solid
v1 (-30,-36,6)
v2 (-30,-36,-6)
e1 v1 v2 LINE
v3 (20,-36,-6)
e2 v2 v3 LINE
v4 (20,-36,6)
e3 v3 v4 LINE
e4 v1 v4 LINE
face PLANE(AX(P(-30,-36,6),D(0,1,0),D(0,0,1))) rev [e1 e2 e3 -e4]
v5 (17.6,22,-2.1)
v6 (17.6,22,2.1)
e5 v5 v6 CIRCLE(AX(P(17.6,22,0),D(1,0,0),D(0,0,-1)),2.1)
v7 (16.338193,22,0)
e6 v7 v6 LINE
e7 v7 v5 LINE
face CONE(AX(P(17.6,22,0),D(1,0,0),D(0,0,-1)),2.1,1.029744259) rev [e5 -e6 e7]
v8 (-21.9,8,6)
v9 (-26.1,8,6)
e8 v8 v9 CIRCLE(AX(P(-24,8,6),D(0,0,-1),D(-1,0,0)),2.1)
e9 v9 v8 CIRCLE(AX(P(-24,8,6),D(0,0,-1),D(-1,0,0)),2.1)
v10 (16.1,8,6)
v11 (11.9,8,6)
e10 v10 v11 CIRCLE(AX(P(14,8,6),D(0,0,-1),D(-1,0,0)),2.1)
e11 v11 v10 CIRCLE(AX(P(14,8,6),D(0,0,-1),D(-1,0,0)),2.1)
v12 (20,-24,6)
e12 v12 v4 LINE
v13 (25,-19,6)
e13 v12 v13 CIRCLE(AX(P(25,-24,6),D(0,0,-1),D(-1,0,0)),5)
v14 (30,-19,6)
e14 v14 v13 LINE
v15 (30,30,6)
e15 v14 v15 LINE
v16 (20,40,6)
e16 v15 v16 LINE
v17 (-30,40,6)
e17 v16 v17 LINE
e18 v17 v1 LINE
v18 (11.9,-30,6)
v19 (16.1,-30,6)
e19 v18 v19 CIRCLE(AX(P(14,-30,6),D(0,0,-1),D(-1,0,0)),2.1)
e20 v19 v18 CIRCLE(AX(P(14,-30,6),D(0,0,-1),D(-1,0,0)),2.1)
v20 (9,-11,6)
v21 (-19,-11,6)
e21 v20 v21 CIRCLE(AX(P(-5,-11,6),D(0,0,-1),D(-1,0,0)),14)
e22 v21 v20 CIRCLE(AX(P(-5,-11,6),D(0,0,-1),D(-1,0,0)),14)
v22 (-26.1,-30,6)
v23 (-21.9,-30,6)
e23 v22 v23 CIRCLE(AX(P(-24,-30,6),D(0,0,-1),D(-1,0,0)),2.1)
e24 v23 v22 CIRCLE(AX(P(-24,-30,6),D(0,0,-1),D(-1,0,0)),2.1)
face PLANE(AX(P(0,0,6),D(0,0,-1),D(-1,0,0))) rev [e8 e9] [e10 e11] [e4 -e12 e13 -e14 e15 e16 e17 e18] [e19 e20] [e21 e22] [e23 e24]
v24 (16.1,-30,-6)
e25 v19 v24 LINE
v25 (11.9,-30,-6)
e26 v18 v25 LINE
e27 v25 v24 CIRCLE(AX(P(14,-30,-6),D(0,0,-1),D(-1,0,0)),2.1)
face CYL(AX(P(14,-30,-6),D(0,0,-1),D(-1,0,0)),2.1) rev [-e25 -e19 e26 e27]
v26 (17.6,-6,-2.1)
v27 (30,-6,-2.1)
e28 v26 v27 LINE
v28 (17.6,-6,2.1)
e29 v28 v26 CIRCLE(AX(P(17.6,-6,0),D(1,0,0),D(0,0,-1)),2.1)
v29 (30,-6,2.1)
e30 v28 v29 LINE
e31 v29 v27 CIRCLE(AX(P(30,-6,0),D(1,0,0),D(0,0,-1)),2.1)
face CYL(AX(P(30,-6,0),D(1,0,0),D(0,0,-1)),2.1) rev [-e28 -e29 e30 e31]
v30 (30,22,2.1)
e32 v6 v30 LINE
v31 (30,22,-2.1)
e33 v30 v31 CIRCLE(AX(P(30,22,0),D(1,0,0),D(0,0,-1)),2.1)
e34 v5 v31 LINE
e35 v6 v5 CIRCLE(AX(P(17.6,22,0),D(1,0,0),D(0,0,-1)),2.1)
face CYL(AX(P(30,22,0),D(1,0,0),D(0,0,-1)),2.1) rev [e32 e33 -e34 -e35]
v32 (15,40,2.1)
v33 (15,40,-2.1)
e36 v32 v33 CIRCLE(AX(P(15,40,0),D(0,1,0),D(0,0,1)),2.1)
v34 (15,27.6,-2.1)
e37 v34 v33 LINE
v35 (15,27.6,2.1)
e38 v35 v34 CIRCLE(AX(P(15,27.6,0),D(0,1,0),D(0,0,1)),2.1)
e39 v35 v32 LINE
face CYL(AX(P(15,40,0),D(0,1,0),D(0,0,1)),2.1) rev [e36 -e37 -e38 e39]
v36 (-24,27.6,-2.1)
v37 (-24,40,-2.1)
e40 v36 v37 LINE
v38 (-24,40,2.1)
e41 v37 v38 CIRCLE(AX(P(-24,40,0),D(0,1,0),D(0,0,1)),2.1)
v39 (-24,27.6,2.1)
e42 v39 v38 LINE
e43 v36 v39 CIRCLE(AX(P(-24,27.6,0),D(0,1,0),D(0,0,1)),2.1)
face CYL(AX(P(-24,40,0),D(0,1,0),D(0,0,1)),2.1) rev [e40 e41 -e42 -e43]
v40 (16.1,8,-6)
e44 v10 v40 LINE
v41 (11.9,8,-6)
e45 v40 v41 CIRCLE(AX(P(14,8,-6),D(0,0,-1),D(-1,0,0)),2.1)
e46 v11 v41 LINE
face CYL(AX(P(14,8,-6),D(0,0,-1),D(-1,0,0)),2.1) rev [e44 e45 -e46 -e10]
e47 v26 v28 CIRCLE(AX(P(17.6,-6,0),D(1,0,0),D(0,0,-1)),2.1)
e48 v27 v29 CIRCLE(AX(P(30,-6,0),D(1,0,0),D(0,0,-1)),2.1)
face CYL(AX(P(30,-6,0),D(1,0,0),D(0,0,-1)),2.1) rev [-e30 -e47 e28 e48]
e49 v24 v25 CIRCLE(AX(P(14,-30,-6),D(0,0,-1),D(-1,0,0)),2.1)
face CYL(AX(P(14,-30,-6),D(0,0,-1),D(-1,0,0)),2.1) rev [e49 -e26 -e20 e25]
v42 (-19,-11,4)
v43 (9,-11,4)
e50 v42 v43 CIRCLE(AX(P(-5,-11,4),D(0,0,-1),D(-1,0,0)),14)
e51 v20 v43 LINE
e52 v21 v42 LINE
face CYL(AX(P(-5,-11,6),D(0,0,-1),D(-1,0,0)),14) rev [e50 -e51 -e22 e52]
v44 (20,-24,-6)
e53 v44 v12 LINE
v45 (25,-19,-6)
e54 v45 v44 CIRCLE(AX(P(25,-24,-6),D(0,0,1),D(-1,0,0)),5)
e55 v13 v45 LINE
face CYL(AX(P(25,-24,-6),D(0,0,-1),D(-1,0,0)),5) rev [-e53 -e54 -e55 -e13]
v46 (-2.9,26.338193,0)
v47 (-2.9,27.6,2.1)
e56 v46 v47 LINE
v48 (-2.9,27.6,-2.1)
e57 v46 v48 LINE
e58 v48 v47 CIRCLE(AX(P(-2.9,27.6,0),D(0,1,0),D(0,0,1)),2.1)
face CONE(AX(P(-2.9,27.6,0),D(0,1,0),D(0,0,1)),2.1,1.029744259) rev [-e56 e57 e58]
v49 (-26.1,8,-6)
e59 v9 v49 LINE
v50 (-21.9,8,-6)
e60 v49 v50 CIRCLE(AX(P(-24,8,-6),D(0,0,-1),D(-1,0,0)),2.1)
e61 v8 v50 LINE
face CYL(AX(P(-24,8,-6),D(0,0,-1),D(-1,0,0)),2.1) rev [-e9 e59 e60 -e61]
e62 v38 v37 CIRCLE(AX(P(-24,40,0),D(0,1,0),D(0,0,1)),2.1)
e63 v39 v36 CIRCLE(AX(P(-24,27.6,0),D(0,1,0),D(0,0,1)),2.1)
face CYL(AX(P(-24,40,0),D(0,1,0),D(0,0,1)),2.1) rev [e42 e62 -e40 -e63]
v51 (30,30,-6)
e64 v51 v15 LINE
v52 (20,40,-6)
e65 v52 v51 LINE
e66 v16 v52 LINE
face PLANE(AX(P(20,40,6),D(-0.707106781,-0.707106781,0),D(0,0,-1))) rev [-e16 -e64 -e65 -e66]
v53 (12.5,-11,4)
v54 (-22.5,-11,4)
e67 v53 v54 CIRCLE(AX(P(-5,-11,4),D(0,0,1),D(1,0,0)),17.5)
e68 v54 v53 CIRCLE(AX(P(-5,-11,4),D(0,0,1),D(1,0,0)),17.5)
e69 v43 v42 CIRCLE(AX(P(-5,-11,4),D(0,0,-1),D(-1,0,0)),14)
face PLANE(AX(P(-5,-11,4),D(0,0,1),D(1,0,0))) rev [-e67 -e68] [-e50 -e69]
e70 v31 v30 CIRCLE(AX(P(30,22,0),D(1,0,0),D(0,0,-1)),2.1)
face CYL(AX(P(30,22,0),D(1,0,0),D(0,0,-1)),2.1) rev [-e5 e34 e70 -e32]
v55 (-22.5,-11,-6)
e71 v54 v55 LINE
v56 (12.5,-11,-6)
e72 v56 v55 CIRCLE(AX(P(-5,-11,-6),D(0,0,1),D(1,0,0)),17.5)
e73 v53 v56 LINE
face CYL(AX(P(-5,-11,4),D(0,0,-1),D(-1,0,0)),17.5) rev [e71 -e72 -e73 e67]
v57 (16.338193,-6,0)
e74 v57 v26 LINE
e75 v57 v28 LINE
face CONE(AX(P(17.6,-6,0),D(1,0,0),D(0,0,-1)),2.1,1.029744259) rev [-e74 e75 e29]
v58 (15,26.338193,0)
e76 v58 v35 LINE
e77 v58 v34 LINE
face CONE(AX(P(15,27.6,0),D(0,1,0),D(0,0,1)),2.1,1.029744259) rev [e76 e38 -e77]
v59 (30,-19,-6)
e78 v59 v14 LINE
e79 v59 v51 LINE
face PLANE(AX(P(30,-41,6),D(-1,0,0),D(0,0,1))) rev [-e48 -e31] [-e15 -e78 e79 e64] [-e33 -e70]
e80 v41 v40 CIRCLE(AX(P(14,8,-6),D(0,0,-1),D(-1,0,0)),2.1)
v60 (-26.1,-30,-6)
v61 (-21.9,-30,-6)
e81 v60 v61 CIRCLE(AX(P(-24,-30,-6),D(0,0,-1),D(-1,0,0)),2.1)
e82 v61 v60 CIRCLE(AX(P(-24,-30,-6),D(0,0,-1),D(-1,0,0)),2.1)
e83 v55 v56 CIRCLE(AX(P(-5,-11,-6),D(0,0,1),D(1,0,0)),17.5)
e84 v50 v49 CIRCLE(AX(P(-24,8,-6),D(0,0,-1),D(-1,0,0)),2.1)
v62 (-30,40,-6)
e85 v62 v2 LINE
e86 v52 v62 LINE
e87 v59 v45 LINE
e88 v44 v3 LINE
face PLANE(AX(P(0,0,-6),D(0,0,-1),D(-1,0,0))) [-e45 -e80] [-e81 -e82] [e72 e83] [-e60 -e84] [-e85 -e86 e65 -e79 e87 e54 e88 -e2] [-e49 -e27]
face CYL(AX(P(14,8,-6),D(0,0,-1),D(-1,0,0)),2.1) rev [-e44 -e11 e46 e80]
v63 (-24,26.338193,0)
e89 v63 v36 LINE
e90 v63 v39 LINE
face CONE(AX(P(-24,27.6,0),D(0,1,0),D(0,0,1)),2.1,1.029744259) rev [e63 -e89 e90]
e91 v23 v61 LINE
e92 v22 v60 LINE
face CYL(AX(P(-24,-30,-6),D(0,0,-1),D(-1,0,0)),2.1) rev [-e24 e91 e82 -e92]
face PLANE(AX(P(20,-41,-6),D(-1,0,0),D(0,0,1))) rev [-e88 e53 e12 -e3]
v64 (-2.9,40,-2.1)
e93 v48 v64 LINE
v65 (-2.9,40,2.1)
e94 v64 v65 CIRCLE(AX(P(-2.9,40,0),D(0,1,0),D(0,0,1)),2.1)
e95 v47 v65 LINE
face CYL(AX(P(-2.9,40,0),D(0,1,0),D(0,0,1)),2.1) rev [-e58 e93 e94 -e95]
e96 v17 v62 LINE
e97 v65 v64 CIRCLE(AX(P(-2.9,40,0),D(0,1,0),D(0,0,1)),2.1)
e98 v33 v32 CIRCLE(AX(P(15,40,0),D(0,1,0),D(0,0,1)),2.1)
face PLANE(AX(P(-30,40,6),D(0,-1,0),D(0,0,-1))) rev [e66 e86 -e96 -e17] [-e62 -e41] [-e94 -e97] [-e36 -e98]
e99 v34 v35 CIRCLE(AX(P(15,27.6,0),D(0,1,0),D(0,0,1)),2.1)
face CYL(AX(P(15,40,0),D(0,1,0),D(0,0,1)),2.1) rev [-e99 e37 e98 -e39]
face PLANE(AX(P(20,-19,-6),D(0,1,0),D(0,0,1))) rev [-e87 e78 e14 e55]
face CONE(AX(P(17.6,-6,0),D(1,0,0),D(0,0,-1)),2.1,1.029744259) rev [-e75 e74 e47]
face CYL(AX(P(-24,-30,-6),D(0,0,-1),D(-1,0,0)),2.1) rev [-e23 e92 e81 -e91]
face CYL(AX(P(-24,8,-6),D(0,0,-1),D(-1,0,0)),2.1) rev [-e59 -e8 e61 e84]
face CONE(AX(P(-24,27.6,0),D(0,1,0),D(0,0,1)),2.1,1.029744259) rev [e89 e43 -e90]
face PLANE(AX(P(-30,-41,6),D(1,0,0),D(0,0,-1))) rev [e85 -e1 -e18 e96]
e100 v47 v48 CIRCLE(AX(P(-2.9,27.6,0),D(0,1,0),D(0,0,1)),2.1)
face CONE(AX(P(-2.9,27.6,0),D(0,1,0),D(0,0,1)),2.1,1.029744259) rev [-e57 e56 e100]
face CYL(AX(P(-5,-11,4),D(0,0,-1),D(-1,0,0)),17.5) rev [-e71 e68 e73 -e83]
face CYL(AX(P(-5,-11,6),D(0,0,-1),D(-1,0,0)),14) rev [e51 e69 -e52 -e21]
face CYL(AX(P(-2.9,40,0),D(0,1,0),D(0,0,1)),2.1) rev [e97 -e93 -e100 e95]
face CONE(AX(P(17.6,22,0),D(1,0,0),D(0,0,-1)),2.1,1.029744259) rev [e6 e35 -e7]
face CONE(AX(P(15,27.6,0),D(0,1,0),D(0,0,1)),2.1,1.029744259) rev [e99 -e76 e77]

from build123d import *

# Parameters (mm, degrees)
SKETCH_1_W             = 60
SKETCH_1_H             = 82
EXTRUDE_1_DEPTH        = 6
SKETCH_10_R            = 17.5
CUT_EXTRUDE_1_DEPTH    = 10
SKETCH_12_R            = 14
CUT_EXTRUDE_2_DEPTH    = 52.778373864
SKETCH_13_W            = 10
SKETCH_13_H            = 22
CUT_EXTRUDE_3_DEPTH    = 53.201532545
FILLET_1_R             = 5
HOLE_WIZARD_M5_2_D     = 4.2
MOVE_FACE_1_BY         = 1
CHAMFER_2_SIZE         = 10
HOLE_WIZARD_M5_3_D     = 4.2
HOLE_WIZARD_M5_3_DEPTH = 12.4
HOLE_WIZARD_M5_3_TIP   = 1.2618073
HOLE_WIZARD_M5_4_D     = 4.2
HOLE_WIZARD_M5_4_DEPTH = 12.4
HOLE_WIZARD_M5_4_TIP   = 1.2618073
MOVE_FACE_3_BY         = 5


with BuildPart() as part:
    # 草图1 → 凸台-拉伸1 (new, symmetric)
    with BuildSketch(Plane.XY):
        Rectangle(SKETCH_1_W, SKETCH_1_H)
    extrude(amount=EXTRUDE_1_DEPTH, both=True)

    # 草图10 → 切除-拉伸1 (cut)
    with BuildSketch(Plane.XY.offset(-6)):
        with Locations((-5, -11)):
            Circle(SKETCH_10_R)
    extrude(amount=CUT_EXTRUDE_1_DEPTH, mode=Mode.SUBTRACT)

    # 草图12 → 切除-拉伸2 (cut, through all)
    with BuildSketch(Plane(origin=(0, 0, 4), x_dir=(-1, 0, 0), z_dir=(0, 0, -1))):
        with Locations((5, -11)):
            Circle(SKETCH_12_R)
    extrude(amount=-CUT_EXTRUDE_2_DEPTH, mode=Mode.SUBTRACT)

    # 草图13 → 切除-拉伸3 (cut, through all)
    with BuildSketch(Plane.XY.offset(6)):
        with Locations((25, -30)):
            Rectangle(SKETCH_13_W, SKETCH_13_H)
    extrude(amount=-CUT_EXTRUDE_3_DEPTH, mode=Mode.SUBTRACT)

    # 圆角1
    fillet_1_edges = [part.edges().sort_by_distance(p)[0] for p in [
        (20, -19, 0),
    ]]
    fillet(fillet_1_edges, radius=FILLET_1_R)

    # M5 螺纹孔2 (through all)
    with Locations(Plane(origin=(0, 0, -6), x_dir=(-1, 0, 0), z_dir=(0, 0, -1))):
        with Locations((-14, 8), (-14, -30), (24, -30), (24, 8)):
            Hole(HOLE_WIZARD_M5_2_D / 2)

    # Move Face 1: a face moved inward by 1.0
    extrude(part.faces().sort_by_distance((0, 41, 0))[0], amount=MOVE_FACE_1_BY, dir=(0, -1, 0), mode=Mode.SUBTRACT)

    # 倒角2
    chamfer_2_edges = [part.edges().sort_by_distance(p)[0] for p in [
        (30, 40, 0),
    ]]
    chamfer(chamfer_2_edges, length=CHAMFER_2_SIZE)

    # M5 螺纹孔3
    with Locations(Plane(origin=(0, 40, 0), x_dir=(1, 0, 0), z_dir=(0, 1, 0))):
        with Locations((-24, 0), (-2.9, 0), (15, 0)):
            Hole(HOLE_WIZARD_M5_3_D / 2, depth=HOLE_WIZARD_M5_3_DEPTH)
            with Locations((0, 0, -(HOLE_WIZARD_M5_3_DEPTH + HOLE_WIZARD_M5_3_TIP / 2))):  # 118° drill point
                Cone(0, HOLE_WIZARD_M5_3_D / 2, HOLE_WIZARD_M5_3_TIP, mode=Mode.SUBTRACT)

    # M5 螺纹孔4
    with Locations(Plane(origin=(30, 0, 0), x_dir=(0, 0, -1), z_dir=(1, 0, 0))):
        with Locations((0, 22), (0, -6)):
            Hole(HOLE_WIZARD_M5_4_D / 2, depth=HOLE_WIZARD_M5_4_DEPTH)
            with Locations((0, 0, -(HOLE_WIZARD_M5_4_DEPTH + HOLE_WIZARD_M5_4_TIP / 2))):  # 118° drill point
                Cone(0, HOLE_WIZARD_M5_4_D / 2, HOLE_WIZARD_M5_4_TIP, mode=Mode.SUBTRACT)

    # Move Face 3: a face moved inward by 5.0
    extrude(part.faces().sort_by_distance((-5, -41, 0))[0], amount=MOVE_FACE_3_BY, dir=(0, 1, 0), mode=Mode.SUBTRACT)


solid = part.part
